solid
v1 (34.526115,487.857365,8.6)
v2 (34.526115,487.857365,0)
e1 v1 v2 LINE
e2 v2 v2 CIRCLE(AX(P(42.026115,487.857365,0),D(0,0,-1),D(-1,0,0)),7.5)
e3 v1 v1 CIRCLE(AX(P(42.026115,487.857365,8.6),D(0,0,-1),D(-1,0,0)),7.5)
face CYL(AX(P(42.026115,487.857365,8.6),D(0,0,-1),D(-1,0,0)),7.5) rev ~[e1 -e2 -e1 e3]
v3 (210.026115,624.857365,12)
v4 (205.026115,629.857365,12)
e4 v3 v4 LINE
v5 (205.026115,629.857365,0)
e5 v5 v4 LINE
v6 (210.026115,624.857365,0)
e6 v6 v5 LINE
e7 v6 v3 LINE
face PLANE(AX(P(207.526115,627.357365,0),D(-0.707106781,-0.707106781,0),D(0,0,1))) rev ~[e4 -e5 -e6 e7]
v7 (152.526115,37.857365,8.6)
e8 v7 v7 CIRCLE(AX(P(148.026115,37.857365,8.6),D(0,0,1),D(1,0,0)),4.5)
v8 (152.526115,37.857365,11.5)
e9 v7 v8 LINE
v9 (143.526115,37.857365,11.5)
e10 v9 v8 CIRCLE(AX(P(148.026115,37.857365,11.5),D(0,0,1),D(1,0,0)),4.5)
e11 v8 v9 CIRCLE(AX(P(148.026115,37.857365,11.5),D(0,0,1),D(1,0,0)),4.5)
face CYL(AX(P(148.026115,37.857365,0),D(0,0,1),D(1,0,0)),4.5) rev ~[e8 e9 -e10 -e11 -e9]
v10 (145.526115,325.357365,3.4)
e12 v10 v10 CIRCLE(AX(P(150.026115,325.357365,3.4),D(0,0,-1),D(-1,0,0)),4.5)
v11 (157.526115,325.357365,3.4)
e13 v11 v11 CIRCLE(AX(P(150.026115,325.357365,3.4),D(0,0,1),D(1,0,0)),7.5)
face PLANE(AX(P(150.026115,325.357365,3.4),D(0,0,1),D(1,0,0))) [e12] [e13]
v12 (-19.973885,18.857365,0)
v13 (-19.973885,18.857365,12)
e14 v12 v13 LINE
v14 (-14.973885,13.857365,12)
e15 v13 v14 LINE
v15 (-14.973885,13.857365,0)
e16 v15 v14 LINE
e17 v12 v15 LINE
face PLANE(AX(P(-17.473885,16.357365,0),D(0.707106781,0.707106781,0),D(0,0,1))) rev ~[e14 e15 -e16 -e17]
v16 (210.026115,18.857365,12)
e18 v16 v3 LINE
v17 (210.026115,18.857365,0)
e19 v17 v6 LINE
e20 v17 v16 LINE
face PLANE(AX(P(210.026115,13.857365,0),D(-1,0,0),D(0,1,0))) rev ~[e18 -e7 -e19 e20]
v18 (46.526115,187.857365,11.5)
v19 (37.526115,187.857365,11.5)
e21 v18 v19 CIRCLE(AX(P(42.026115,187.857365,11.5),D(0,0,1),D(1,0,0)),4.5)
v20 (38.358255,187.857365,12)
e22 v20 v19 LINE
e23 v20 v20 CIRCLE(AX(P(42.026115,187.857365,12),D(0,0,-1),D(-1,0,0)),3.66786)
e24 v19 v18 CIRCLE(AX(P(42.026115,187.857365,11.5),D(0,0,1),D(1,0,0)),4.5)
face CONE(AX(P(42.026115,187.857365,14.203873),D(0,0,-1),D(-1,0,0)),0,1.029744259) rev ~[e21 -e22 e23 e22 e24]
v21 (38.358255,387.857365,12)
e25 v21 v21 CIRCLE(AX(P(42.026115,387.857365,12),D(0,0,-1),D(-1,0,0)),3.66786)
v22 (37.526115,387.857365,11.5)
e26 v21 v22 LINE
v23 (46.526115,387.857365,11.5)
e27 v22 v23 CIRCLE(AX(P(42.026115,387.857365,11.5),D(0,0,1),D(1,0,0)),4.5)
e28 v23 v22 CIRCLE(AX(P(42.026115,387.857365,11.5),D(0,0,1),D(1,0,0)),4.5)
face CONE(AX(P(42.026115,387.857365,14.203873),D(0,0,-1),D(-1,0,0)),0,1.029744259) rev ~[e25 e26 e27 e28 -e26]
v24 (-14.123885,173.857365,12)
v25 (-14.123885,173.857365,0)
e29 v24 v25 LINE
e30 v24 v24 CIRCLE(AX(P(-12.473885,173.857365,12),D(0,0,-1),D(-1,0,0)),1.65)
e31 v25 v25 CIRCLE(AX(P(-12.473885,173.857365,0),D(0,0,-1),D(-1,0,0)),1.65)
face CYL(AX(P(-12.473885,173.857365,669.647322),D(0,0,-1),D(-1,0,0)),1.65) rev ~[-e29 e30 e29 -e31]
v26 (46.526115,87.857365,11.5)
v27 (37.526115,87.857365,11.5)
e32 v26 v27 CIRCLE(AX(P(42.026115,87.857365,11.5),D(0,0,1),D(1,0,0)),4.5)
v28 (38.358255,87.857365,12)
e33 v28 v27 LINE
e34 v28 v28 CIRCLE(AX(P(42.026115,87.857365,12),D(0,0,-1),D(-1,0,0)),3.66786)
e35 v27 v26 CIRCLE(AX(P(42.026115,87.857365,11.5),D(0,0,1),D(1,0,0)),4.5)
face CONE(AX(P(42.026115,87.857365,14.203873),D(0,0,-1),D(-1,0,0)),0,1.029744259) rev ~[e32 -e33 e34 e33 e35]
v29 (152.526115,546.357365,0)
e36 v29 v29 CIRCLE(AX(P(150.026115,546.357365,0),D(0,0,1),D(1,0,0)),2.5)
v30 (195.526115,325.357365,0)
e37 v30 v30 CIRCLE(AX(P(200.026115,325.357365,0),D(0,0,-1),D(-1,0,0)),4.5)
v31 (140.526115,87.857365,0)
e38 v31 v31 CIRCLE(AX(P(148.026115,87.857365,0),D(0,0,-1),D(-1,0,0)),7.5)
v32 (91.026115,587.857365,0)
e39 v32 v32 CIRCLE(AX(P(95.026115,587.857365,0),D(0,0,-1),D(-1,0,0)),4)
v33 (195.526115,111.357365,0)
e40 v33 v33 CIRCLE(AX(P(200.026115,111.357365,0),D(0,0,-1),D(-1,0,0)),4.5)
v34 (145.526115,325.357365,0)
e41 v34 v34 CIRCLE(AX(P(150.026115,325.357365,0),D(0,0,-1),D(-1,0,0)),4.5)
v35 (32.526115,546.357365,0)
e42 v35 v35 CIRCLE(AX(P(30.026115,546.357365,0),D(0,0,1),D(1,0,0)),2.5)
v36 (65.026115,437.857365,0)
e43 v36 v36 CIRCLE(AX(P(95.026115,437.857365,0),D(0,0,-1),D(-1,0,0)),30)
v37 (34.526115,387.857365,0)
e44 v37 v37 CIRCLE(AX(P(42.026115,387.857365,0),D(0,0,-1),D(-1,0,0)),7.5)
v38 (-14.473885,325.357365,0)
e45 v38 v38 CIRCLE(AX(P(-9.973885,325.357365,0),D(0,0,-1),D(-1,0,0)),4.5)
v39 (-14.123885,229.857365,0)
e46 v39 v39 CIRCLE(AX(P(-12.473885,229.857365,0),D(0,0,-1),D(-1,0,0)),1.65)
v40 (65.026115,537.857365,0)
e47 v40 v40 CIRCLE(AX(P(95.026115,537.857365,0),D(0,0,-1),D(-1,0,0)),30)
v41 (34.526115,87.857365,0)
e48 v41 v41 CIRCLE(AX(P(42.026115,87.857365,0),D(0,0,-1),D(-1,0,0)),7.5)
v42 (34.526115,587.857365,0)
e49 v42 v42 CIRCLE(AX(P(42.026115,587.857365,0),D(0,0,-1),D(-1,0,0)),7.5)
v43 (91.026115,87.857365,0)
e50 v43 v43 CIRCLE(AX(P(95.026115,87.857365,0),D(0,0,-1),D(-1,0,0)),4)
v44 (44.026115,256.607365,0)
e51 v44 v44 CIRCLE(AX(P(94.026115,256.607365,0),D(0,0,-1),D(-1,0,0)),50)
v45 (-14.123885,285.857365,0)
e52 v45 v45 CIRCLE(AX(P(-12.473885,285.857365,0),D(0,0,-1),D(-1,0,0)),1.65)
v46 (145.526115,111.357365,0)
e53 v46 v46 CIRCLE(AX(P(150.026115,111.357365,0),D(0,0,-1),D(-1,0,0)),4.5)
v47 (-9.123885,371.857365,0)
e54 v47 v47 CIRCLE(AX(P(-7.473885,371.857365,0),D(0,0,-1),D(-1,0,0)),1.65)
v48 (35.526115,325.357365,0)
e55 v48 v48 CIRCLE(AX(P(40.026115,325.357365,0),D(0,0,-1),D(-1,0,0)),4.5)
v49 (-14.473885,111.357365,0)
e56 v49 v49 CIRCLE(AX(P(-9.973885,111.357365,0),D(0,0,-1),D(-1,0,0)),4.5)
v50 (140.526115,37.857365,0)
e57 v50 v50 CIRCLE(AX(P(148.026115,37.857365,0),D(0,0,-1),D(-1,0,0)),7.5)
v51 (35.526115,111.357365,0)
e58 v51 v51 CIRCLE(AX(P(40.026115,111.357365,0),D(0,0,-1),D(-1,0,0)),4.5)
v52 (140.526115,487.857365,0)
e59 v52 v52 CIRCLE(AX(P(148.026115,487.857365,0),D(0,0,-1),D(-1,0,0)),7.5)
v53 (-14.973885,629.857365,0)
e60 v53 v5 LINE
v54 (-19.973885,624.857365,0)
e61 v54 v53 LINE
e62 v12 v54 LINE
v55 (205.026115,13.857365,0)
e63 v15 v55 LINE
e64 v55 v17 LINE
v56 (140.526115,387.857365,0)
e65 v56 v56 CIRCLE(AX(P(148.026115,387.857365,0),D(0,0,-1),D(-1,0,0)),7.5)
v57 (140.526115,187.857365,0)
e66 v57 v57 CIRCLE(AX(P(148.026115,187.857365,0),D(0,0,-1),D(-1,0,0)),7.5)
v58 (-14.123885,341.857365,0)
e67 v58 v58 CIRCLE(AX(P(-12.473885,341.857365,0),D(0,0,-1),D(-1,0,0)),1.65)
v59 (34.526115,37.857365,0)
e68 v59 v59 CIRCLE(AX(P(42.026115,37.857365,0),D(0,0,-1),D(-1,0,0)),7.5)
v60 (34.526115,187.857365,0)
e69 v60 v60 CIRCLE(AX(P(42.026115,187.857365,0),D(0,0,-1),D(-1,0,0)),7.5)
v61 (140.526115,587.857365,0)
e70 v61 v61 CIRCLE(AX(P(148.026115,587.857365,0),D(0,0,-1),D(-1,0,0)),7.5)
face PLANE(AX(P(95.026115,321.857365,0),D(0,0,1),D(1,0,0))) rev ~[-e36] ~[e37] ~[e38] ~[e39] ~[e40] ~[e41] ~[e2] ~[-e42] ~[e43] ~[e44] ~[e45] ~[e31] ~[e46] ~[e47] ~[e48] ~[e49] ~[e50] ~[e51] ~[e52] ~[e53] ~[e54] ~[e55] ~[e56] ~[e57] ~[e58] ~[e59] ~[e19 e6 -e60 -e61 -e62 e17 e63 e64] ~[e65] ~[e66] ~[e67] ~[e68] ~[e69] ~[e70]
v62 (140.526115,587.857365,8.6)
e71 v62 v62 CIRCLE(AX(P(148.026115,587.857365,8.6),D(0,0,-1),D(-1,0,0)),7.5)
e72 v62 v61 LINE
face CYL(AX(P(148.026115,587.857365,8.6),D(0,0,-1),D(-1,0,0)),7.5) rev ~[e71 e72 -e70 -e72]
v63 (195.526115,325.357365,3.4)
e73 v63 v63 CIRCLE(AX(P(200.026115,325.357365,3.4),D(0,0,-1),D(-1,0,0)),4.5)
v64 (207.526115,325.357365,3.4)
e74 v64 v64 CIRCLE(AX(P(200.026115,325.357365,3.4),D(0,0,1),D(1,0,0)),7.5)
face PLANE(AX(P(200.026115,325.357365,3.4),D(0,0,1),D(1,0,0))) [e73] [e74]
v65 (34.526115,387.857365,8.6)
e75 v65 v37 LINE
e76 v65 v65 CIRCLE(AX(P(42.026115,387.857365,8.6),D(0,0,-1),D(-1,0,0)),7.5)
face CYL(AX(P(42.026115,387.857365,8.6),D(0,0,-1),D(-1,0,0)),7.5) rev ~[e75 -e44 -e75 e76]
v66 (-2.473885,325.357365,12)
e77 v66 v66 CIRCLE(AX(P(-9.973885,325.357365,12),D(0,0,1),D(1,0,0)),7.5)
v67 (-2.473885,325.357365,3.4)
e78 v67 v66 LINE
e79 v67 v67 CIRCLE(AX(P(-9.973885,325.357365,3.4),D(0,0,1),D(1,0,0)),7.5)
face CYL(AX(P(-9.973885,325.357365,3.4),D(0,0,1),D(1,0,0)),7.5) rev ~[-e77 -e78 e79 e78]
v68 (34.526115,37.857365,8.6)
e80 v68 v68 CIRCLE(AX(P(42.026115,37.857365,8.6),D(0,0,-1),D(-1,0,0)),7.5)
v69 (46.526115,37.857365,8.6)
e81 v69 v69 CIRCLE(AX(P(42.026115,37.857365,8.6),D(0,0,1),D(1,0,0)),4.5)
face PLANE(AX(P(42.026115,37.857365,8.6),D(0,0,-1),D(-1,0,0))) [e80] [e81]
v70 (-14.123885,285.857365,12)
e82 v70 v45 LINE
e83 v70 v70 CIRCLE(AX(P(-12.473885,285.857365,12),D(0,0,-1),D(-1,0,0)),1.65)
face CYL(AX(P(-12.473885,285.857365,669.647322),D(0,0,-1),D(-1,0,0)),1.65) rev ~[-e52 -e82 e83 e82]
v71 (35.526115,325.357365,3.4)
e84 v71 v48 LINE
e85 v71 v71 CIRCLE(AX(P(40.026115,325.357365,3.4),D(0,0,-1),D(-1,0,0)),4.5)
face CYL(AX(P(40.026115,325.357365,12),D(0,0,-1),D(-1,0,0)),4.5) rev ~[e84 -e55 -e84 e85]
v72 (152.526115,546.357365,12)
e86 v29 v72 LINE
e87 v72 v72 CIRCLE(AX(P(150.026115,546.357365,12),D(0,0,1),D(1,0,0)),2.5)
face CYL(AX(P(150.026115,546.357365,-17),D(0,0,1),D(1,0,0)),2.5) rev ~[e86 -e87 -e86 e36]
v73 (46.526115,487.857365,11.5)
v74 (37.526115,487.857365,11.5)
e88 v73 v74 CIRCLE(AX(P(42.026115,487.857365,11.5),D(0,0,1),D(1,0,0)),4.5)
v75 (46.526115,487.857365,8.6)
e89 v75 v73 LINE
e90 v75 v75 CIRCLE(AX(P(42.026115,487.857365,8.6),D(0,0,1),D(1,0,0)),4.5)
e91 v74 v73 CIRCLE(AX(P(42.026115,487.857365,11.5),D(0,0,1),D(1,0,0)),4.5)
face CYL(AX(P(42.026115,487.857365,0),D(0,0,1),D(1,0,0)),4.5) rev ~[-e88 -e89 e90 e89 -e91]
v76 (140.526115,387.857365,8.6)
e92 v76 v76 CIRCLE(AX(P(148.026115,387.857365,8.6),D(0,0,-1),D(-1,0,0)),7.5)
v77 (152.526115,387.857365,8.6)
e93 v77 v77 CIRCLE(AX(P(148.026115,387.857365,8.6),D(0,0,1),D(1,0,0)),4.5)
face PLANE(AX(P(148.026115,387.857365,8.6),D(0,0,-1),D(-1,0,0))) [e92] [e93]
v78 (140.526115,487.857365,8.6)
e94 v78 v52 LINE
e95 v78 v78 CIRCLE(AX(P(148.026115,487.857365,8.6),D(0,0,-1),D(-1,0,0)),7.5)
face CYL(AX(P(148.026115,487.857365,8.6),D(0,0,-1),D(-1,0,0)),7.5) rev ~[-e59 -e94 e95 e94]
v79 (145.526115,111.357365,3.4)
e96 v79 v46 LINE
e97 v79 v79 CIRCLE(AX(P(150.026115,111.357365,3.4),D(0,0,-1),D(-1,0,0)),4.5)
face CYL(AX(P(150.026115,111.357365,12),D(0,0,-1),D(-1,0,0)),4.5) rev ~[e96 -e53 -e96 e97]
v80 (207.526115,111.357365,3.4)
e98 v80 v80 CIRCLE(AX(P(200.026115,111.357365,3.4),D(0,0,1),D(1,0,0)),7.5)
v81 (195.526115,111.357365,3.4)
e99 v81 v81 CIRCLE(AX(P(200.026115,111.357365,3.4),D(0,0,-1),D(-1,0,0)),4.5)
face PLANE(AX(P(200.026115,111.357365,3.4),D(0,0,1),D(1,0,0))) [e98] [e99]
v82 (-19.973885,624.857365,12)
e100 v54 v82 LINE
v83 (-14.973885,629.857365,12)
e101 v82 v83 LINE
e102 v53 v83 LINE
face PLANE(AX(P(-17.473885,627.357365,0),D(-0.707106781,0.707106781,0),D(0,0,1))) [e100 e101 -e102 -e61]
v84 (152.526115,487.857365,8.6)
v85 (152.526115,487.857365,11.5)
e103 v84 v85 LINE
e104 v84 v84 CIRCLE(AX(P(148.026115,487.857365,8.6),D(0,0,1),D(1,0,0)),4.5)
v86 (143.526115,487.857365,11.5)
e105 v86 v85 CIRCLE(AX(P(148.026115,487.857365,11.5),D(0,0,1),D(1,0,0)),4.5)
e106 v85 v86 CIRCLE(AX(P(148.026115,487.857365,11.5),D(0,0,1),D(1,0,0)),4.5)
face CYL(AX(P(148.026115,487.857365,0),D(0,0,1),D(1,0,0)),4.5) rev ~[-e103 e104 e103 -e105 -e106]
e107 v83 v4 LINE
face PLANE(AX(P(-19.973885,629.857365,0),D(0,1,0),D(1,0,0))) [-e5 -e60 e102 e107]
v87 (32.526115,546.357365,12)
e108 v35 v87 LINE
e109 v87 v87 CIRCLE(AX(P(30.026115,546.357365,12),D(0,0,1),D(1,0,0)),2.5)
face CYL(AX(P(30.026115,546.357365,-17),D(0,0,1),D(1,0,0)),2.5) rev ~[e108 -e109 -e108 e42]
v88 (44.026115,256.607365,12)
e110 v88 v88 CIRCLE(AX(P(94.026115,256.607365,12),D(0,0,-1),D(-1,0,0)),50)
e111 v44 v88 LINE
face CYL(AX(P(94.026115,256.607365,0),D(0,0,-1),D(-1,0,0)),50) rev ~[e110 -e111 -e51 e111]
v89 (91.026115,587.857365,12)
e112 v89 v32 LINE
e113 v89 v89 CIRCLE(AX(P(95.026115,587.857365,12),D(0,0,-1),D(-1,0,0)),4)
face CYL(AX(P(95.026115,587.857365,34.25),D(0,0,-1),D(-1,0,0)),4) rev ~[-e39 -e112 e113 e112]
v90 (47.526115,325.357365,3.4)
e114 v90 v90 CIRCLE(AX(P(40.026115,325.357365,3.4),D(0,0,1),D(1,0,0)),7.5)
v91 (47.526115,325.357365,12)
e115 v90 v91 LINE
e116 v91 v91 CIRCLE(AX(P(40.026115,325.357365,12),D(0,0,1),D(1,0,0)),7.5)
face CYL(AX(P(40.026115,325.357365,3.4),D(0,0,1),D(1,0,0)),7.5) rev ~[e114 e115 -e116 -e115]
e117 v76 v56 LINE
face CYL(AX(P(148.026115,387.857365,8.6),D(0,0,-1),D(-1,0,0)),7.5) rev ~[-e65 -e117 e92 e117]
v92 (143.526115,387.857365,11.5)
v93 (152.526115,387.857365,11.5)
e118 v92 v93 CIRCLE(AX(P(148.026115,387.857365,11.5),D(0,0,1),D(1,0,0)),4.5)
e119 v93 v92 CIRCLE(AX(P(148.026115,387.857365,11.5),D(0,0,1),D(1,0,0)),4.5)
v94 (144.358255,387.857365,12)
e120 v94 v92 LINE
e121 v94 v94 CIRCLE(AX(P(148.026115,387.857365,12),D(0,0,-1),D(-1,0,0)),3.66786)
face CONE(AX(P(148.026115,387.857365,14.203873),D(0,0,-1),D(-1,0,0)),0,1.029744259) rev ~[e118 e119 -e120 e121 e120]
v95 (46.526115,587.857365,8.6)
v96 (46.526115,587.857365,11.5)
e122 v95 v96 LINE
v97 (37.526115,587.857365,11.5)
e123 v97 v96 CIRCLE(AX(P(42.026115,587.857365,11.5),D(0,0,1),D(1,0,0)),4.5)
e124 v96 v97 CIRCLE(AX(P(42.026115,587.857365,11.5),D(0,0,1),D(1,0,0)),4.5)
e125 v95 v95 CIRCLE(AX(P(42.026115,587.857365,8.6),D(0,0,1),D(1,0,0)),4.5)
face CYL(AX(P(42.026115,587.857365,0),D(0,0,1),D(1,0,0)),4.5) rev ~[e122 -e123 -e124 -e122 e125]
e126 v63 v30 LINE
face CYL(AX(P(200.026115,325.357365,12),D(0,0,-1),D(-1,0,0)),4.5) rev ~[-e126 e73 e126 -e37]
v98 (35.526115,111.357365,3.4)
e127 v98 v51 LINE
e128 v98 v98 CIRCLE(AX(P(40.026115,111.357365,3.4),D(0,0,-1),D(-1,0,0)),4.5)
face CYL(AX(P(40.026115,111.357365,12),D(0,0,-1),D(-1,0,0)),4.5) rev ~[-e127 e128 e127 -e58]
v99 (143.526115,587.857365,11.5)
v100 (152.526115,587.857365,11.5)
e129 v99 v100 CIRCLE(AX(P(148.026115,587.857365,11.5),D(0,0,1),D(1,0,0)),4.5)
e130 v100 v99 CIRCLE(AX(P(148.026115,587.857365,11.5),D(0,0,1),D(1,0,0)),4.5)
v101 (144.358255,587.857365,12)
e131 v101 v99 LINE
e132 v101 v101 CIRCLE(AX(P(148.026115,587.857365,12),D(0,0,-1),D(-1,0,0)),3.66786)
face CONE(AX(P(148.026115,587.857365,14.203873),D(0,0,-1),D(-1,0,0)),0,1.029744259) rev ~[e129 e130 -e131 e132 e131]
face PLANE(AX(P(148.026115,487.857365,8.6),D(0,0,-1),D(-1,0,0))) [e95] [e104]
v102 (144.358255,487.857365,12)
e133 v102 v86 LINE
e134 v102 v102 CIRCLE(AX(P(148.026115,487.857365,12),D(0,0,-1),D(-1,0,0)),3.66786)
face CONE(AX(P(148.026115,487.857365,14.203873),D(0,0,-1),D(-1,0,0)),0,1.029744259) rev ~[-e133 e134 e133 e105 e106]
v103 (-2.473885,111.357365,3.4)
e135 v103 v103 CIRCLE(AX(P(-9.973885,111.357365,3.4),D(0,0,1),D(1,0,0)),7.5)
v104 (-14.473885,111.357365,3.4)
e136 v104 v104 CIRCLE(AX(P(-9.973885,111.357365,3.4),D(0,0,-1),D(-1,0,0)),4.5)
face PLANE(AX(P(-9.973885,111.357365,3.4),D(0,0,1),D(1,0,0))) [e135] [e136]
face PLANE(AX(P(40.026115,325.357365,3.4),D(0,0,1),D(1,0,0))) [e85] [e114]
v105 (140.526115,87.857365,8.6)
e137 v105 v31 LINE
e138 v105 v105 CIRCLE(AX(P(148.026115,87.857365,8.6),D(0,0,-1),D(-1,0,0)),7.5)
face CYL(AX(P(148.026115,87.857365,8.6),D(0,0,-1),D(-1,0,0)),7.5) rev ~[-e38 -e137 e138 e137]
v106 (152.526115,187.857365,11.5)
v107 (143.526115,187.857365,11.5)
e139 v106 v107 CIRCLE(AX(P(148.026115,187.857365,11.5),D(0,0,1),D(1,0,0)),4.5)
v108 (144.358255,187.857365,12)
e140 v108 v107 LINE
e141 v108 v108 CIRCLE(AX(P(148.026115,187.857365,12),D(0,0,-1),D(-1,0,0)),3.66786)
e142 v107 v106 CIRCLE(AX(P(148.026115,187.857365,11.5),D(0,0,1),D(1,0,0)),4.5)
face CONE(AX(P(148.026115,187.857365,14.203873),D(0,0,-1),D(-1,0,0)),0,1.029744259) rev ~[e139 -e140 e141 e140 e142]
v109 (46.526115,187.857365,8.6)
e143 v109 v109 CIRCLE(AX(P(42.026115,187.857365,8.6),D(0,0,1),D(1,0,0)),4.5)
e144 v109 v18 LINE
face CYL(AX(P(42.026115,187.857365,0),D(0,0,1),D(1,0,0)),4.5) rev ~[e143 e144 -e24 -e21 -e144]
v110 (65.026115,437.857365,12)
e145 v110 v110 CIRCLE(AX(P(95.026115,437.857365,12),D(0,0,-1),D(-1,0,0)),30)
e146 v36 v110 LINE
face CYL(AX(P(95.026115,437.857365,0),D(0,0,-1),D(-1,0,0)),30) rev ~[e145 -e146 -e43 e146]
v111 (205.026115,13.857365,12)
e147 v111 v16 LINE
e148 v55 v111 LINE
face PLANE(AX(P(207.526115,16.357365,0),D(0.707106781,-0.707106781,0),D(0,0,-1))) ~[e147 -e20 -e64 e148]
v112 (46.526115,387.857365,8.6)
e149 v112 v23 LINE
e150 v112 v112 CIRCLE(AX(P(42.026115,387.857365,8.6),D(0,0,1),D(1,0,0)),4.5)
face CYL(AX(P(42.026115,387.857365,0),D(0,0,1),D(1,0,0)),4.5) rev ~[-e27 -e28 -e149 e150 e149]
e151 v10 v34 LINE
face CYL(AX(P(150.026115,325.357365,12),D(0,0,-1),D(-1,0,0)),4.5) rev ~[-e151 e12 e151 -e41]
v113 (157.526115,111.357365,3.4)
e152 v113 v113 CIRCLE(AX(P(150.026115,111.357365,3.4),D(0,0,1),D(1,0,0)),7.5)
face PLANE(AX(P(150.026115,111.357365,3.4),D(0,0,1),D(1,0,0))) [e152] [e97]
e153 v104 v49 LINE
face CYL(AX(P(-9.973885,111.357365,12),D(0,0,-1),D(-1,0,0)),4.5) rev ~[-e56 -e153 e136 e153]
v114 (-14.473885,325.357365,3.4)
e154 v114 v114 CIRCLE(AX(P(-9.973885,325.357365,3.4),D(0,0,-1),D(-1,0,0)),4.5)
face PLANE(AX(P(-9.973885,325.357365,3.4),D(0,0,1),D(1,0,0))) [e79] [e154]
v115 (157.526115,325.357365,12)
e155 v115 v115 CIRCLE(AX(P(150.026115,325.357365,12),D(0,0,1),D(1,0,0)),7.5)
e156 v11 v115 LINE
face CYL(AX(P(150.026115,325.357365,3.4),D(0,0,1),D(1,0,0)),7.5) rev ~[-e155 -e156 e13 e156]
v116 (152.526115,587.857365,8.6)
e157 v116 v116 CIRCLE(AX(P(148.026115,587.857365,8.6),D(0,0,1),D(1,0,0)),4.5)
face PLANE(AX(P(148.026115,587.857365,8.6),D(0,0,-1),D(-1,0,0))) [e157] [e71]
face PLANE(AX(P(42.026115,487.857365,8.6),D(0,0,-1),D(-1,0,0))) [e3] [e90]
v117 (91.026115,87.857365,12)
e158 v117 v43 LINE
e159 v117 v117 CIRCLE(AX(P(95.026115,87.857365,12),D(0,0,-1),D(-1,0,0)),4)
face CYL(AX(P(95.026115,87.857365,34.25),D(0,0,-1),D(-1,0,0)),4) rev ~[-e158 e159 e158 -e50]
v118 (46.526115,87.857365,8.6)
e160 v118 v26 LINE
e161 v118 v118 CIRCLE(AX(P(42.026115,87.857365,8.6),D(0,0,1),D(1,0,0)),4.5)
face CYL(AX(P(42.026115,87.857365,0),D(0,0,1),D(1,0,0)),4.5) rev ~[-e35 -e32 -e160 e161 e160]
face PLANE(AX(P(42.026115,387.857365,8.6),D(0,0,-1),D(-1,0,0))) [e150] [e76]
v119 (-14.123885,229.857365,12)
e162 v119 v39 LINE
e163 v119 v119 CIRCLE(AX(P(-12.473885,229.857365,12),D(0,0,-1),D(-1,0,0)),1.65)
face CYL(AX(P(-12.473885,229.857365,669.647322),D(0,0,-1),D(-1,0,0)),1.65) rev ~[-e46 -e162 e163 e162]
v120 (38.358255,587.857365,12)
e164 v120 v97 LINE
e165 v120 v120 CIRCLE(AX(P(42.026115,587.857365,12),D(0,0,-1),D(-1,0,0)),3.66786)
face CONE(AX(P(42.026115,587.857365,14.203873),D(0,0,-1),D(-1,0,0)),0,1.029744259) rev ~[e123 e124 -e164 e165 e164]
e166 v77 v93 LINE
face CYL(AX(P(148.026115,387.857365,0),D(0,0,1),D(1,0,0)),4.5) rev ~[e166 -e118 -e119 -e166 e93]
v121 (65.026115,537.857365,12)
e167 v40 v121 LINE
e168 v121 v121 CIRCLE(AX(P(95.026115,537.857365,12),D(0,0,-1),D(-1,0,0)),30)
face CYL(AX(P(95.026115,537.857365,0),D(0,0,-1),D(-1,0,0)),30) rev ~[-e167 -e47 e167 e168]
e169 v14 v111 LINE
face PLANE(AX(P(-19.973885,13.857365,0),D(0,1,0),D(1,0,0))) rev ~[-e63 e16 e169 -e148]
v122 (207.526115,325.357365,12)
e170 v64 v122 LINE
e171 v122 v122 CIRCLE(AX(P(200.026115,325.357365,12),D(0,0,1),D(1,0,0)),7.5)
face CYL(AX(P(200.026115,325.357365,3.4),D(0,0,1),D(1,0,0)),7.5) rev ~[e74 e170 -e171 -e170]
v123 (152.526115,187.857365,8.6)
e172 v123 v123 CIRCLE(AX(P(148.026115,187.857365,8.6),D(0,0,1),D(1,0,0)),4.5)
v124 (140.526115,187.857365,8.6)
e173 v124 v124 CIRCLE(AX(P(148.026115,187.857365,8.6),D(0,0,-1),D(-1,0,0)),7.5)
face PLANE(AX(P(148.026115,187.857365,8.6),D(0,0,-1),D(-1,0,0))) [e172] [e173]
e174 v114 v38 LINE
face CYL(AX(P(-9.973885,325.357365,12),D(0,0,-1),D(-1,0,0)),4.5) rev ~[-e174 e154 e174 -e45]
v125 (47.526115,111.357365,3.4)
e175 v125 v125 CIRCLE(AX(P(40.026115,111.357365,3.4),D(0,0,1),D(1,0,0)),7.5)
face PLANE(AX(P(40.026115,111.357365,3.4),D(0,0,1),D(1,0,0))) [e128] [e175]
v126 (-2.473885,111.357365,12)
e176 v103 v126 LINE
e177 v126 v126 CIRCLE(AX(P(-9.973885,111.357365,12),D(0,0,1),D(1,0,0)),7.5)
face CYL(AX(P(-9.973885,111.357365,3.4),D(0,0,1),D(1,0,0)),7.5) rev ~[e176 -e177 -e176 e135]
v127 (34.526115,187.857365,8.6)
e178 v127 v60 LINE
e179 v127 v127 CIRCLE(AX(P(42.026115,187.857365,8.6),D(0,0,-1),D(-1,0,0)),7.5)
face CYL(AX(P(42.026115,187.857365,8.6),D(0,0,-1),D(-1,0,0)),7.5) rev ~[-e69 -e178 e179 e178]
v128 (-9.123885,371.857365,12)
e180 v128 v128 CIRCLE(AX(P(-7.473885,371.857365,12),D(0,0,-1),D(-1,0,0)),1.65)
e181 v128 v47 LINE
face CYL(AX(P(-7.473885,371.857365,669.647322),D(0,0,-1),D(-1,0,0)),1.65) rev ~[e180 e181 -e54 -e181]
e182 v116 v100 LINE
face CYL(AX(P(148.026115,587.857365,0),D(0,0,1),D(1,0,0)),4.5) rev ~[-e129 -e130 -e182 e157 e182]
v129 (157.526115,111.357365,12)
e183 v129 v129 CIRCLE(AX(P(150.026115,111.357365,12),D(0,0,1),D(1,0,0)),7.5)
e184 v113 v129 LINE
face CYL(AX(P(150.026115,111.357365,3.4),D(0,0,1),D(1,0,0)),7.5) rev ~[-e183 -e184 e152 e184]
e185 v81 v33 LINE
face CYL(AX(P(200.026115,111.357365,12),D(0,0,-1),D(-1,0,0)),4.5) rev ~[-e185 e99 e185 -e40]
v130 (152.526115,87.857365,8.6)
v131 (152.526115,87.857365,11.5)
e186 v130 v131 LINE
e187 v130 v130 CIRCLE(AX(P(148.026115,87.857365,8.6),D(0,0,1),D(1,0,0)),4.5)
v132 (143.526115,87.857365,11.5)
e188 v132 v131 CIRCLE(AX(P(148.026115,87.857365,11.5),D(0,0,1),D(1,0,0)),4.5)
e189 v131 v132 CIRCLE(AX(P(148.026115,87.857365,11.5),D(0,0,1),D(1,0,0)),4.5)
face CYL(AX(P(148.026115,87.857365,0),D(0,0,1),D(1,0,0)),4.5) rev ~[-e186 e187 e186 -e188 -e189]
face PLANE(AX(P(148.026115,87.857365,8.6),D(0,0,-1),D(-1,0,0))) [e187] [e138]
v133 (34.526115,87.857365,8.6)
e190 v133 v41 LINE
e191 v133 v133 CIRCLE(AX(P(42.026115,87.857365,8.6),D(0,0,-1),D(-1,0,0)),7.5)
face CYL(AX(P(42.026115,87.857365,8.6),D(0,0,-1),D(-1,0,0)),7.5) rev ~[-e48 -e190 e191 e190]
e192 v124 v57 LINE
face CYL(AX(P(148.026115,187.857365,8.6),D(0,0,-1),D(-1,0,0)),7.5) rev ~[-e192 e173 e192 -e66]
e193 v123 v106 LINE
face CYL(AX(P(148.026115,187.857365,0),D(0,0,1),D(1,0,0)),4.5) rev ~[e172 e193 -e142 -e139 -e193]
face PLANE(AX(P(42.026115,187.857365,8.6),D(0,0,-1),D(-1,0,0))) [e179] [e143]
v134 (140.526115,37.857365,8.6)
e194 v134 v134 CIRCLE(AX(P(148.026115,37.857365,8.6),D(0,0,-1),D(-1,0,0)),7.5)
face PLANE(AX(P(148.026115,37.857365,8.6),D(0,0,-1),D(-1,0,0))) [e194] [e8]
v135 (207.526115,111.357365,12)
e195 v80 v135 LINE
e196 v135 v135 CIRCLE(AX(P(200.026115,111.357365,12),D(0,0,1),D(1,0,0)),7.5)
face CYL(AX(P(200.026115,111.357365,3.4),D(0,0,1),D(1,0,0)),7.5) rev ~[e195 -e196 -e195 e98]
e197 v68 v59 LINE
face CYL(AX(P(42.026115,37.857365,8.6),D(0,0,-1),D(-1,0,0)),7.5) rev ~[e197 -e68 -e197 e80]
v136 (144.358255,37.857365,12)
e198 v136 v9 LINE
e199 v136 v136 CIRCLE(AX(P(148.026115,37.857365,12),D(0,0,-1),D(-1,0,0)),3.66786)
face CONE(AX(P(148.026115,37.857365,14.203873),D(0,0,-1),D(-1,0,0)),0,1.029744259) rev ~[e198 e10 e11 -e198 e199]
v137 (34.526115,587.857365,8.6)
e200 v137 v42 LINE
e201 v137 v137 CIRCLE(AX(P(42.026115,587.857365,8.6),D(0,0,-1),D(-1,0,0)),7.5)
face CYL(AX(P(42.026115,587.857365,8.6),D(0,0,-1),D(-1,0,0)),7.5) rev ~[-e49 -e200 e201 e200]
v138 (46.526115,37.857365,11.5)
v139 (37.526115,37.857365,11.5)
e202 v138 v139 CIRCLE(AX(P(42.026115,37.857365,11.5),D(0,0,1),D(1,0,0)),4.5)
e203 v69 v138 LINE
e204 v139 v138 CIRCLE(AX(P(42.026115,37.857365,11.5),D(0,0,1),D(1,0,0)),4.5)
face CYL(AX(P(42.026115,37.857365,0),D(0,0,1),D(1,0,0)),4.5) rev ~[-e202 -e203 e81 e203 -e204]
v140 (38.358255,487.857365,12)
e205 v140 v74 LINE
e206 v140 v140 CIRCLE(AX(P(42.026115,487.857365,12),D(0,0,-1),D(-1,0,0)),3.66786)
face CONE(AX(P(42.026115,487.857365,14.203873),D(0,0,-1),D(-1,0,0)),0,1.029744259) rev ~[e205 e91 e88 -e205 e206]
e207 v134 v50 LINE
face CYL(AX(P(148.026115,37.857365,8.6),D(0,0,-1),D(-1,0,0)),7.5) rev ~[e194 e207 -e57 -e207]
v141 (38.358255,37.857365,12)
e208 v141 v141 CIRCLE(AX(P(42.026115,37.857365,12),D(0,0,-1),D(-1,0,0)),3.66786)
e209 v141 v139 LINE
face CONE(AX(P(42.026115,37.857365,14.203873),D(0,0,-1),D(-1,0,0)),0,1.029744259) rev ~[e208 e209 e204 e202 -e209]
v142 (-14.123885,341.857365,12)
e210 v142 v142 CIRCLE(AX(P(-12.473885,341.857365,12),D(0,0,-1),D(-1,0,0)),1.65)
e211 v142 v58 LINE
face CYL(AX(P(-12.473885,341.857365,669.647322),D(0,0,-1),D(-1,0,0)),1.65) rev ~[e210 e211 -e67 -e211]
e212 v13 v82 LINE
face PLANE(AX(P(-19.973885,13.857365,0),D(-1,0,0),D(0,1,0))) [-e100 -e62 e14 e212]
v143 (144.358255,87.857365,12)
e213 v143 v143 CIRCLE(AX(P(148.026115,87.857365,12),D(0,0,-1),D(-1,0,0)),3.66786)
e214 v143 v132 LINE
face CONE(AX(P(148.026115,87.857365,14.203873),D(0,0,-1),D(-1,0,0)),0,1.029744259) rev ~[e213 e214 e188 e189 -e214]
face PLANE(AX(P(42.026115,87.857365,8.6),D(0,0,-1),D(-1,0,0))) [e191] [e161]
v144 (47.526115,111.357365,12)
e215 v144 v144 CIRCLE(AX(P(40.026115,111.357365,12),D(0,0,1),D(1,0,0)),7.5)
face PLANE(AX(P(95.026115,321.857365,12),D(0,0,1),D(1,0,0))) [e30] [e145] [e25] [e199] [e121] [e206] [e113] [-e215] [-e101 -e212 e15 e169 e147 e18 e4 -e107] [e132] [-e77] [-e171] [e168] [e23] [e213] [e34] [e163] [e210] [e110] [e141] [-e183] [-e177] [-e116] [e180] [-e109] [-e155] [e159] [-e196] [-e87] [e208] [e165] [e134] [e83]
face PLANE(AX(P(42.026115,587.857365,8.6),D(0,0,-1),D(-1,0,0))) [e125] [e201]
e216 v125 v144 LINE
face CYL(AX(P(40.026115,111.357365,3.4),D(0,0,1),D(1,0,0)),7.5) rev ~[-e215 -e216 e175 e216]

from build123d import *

# Parameters (mm, degrees)
SKETCH_1_W                   = 230
SKETCH_1_H                   = 616
EXTRUDE_1_DEPTH              = 12
CHAMFER_1_SIZE               = 5
HOLE_WIZARD_M8_1_D           = 9
HOLE_WIZARD_M8_1_DEPTH       = 11.5
HOLE_WIZARD_M8_1_CBORE_D     = 15
HOLE_WIZARD_M8_1_CBORE_DEPTH = 8.6
HOLE_WIZARD_M8_1_TIP         = 2.703872786
HOLE_WIZARD_M8_2_D           = 9
HOLE_WIZARD_M8_2_DEPTH       = 22.25
HOLE_WIZARD_M8_2_CBORE_D     = 15
HOLE_WIZARD_M8_2_CBORE_DEPTH = 8.6
HOLE_WIZARD_M8_2_TIP         = 2.703872786
MM_1_D                       = 8
MM_1_DEPTH                   = 22.25
MM_1_TIP                     = 2.403442476
HOLE_WIZARD_M4_1_D           = 3.3
HOLE_WIZARD_M4_2_D           = 3.3
SKETCH_12_R                  = 30
SKETCH_12_R_2                = 50
CUT_EXTRUDE_1_DEPTH          = 665.059688056
HOLE_WIZARD_M6_1_D           = 5
HOLE_WIZARD_M6_1_DEPTH       = 17
HOLE_WIZARD_M6_1_TIP         = 1.502151548


with BuildPart() as part:
    # 草图1 → 凸台-拉伸1 (new body)
    with BuildSketch(Plane.XY):
        with Locations((95.026115454, 321.857364907)):
            Rectangle(SKETCH_1_W, SKETCH_1_H)
    extrude(amount=EXTRUDE_1_DEPTH)

    # 倒角1
    chamfer_1_edges = [part.edges().sort_by_distance(p)[0] for p in [
        (210.026115454, 13.857364907, 6),
        (-19.973884546, 13.857364907, 6),
        (-19.973884546, 629.857364907, 6),
        (210.026115454, 629.857364907, 6),
    ]]
    chamfer(chamfer_1_edges, length=CHAMFER_1_SIZE)

    # M8 六角凹头螺钉的柱形沉头孔1
    with Locations(Plane(origin=(0, 0, 0), x_dir=(-1, 0, 0), z_dir=(0, 0, -1))):
        with Locations((-148.026115454, 587.857364907), (-42.026115454, 587.857364907), (-148.026115454, 487.857364907), (-42.026115454, 487.857364907), (-148.026115454, 387.857364907), (-42.026115454, 387.857364907), (-148.026115454, 187.857364907), (-42.026115454, 187.857364907), (-148.026115454, 87.857364907), (-42.026115454, 87.857364907), (-148.026115454, 37.857364907), (-42.026115454, 37.857364907)):
            CounterBoreHole(HOLE_WIZARD_M8_1_D / 2, HOLE_WIZARD_M8_1_CBORE_D / 2, HOLE_WIZARD_M8_1_CBORE_DEPTH, depth=HOLE_WIZARD_M8_1_DEPTH)
            with Locations((0, 0, -(HOLE_WIZARD_M8_1_DEPTH + HOLE_WIZARD_M8_1_TIP / 2))):  # 118° drill point
                Cone(0, HOLE_WIZARD_M8_1_D / 2, HOLE_WIZARD_M8_1_TIP, mode=Mode.SUBTRACT)

    # M8 六角凹头螺钉的柱形沉头孔2
    with Locations(Plane.XY.offset(12)):
        with Locations((-9.973884546, 325.357364907), (40.026115454, 325.357364907), (150.026115454, 325.357364907), (200.026115454, 325.357364907), (-9.973884546, 111.357364907), (40.026115454, 111.357364907), (150.026115454, 111.357364907), (200.026115454, 111.357364907)):
            CounterBoreHole(HOLE_WIZARD_M8_2_D / 2, HOLE_WIZARD_M8_2_CBORE_D / 2, HOLE_WIZARD_M8_2_CBORE_DEPTH, depth=HOLE_WIZARD_M8_2_DEPTH)
            with Locations((0, 0, -(HOLE_WIZARD_M8_2_DEPTH + HOLE_WIZARD_M8_2_TIP / 2))):  # 118° drill point
                Cone(0, HOLE_WIZARD_M8_2_D / 2, HOLE_WIZARD_M8_2_TIP, mode=Mode.SUBTRACT)

    # 大小mm 暗销孔1
    with Locations(Plane.XY.offset(12)):
        with Locations((95.026115454, 587.857364907), (95.026115454, 87.857364907)):
            Hole(MM_1_D / 2, depth=MM_1_DEPTH)
            with Locations((0, 0, -(MM_1_DEPTH + MM_1_TIP / 2))):  # 118° drill point
                Cone(0, MM_1_D / 2, MM_1_TIP, mode=Mode.SUBTRACT)

    # M4 螺纹孔1 (through all)
    with Locations(Plane.XY.offset(12)):
        with Locations((-12.473884546, 341.857364907), (-12.473884546, 285.857364907), (-12.473884546, 229.857364907), (-12.473884546, 173.857364907)):
            Hole(HOLE_WIZARD_M4_1_D / 2)

    # M4 螺纹孔2 (through all)
    with Locations(Plane.XY.offset(12)):
        with Locations((-7.473884546, 371.857364907)):
            Hole(HOLE_WIZARD_M4_2_D / 2)

    # 草图12 → 切除-拉伸1 (cut, through all)
    with BuildSketch(Plane(origin=(0, 0, 0), x_dir=(-1, 0, 0), z_dir=(0, 0, -1))):
        with Locations((-95.026115454, 537.857364907)):
            Circle(SKETCH_12_R)
        with Locations((-95.026115454, 437.857364907)):
            Circle(SKETCH_12_R)
        with Locations((-94.026115454, 256.607364907)):
            Circle(SKETCH_12_R_2)
    extrude(amount=-CUT_EXTRUDE_1_DEPTH, mode=Mode.SUBTRACT)

    # M6 螺纹孔1
    with Locations(Plane(origin=(0, 0, 0), x_dir=(-1, 0, 0), z_dir=(0, 0, -1))):
        with Locations((-150.026115454, 546.357364907), (-30.026115454, 546.357364907)):
            Hole(HOLE_WIZARD_M6_1_D / 2, depth=HOLE_WIZARD_M6_1_DEPTH)
            with Locations((0, 0, -(HOLE_WIZARD_M6_1_DEPTH + HOLE_WIZARD_M6_1_TIP / 2))):  # 118° drill point
                Cone(0, HOLE_WIZARD_M6_1_D / 2, HOLE_WIZARD_M6_1_TIP, mode=Mode.SUBTRACT)


solid = part.part
